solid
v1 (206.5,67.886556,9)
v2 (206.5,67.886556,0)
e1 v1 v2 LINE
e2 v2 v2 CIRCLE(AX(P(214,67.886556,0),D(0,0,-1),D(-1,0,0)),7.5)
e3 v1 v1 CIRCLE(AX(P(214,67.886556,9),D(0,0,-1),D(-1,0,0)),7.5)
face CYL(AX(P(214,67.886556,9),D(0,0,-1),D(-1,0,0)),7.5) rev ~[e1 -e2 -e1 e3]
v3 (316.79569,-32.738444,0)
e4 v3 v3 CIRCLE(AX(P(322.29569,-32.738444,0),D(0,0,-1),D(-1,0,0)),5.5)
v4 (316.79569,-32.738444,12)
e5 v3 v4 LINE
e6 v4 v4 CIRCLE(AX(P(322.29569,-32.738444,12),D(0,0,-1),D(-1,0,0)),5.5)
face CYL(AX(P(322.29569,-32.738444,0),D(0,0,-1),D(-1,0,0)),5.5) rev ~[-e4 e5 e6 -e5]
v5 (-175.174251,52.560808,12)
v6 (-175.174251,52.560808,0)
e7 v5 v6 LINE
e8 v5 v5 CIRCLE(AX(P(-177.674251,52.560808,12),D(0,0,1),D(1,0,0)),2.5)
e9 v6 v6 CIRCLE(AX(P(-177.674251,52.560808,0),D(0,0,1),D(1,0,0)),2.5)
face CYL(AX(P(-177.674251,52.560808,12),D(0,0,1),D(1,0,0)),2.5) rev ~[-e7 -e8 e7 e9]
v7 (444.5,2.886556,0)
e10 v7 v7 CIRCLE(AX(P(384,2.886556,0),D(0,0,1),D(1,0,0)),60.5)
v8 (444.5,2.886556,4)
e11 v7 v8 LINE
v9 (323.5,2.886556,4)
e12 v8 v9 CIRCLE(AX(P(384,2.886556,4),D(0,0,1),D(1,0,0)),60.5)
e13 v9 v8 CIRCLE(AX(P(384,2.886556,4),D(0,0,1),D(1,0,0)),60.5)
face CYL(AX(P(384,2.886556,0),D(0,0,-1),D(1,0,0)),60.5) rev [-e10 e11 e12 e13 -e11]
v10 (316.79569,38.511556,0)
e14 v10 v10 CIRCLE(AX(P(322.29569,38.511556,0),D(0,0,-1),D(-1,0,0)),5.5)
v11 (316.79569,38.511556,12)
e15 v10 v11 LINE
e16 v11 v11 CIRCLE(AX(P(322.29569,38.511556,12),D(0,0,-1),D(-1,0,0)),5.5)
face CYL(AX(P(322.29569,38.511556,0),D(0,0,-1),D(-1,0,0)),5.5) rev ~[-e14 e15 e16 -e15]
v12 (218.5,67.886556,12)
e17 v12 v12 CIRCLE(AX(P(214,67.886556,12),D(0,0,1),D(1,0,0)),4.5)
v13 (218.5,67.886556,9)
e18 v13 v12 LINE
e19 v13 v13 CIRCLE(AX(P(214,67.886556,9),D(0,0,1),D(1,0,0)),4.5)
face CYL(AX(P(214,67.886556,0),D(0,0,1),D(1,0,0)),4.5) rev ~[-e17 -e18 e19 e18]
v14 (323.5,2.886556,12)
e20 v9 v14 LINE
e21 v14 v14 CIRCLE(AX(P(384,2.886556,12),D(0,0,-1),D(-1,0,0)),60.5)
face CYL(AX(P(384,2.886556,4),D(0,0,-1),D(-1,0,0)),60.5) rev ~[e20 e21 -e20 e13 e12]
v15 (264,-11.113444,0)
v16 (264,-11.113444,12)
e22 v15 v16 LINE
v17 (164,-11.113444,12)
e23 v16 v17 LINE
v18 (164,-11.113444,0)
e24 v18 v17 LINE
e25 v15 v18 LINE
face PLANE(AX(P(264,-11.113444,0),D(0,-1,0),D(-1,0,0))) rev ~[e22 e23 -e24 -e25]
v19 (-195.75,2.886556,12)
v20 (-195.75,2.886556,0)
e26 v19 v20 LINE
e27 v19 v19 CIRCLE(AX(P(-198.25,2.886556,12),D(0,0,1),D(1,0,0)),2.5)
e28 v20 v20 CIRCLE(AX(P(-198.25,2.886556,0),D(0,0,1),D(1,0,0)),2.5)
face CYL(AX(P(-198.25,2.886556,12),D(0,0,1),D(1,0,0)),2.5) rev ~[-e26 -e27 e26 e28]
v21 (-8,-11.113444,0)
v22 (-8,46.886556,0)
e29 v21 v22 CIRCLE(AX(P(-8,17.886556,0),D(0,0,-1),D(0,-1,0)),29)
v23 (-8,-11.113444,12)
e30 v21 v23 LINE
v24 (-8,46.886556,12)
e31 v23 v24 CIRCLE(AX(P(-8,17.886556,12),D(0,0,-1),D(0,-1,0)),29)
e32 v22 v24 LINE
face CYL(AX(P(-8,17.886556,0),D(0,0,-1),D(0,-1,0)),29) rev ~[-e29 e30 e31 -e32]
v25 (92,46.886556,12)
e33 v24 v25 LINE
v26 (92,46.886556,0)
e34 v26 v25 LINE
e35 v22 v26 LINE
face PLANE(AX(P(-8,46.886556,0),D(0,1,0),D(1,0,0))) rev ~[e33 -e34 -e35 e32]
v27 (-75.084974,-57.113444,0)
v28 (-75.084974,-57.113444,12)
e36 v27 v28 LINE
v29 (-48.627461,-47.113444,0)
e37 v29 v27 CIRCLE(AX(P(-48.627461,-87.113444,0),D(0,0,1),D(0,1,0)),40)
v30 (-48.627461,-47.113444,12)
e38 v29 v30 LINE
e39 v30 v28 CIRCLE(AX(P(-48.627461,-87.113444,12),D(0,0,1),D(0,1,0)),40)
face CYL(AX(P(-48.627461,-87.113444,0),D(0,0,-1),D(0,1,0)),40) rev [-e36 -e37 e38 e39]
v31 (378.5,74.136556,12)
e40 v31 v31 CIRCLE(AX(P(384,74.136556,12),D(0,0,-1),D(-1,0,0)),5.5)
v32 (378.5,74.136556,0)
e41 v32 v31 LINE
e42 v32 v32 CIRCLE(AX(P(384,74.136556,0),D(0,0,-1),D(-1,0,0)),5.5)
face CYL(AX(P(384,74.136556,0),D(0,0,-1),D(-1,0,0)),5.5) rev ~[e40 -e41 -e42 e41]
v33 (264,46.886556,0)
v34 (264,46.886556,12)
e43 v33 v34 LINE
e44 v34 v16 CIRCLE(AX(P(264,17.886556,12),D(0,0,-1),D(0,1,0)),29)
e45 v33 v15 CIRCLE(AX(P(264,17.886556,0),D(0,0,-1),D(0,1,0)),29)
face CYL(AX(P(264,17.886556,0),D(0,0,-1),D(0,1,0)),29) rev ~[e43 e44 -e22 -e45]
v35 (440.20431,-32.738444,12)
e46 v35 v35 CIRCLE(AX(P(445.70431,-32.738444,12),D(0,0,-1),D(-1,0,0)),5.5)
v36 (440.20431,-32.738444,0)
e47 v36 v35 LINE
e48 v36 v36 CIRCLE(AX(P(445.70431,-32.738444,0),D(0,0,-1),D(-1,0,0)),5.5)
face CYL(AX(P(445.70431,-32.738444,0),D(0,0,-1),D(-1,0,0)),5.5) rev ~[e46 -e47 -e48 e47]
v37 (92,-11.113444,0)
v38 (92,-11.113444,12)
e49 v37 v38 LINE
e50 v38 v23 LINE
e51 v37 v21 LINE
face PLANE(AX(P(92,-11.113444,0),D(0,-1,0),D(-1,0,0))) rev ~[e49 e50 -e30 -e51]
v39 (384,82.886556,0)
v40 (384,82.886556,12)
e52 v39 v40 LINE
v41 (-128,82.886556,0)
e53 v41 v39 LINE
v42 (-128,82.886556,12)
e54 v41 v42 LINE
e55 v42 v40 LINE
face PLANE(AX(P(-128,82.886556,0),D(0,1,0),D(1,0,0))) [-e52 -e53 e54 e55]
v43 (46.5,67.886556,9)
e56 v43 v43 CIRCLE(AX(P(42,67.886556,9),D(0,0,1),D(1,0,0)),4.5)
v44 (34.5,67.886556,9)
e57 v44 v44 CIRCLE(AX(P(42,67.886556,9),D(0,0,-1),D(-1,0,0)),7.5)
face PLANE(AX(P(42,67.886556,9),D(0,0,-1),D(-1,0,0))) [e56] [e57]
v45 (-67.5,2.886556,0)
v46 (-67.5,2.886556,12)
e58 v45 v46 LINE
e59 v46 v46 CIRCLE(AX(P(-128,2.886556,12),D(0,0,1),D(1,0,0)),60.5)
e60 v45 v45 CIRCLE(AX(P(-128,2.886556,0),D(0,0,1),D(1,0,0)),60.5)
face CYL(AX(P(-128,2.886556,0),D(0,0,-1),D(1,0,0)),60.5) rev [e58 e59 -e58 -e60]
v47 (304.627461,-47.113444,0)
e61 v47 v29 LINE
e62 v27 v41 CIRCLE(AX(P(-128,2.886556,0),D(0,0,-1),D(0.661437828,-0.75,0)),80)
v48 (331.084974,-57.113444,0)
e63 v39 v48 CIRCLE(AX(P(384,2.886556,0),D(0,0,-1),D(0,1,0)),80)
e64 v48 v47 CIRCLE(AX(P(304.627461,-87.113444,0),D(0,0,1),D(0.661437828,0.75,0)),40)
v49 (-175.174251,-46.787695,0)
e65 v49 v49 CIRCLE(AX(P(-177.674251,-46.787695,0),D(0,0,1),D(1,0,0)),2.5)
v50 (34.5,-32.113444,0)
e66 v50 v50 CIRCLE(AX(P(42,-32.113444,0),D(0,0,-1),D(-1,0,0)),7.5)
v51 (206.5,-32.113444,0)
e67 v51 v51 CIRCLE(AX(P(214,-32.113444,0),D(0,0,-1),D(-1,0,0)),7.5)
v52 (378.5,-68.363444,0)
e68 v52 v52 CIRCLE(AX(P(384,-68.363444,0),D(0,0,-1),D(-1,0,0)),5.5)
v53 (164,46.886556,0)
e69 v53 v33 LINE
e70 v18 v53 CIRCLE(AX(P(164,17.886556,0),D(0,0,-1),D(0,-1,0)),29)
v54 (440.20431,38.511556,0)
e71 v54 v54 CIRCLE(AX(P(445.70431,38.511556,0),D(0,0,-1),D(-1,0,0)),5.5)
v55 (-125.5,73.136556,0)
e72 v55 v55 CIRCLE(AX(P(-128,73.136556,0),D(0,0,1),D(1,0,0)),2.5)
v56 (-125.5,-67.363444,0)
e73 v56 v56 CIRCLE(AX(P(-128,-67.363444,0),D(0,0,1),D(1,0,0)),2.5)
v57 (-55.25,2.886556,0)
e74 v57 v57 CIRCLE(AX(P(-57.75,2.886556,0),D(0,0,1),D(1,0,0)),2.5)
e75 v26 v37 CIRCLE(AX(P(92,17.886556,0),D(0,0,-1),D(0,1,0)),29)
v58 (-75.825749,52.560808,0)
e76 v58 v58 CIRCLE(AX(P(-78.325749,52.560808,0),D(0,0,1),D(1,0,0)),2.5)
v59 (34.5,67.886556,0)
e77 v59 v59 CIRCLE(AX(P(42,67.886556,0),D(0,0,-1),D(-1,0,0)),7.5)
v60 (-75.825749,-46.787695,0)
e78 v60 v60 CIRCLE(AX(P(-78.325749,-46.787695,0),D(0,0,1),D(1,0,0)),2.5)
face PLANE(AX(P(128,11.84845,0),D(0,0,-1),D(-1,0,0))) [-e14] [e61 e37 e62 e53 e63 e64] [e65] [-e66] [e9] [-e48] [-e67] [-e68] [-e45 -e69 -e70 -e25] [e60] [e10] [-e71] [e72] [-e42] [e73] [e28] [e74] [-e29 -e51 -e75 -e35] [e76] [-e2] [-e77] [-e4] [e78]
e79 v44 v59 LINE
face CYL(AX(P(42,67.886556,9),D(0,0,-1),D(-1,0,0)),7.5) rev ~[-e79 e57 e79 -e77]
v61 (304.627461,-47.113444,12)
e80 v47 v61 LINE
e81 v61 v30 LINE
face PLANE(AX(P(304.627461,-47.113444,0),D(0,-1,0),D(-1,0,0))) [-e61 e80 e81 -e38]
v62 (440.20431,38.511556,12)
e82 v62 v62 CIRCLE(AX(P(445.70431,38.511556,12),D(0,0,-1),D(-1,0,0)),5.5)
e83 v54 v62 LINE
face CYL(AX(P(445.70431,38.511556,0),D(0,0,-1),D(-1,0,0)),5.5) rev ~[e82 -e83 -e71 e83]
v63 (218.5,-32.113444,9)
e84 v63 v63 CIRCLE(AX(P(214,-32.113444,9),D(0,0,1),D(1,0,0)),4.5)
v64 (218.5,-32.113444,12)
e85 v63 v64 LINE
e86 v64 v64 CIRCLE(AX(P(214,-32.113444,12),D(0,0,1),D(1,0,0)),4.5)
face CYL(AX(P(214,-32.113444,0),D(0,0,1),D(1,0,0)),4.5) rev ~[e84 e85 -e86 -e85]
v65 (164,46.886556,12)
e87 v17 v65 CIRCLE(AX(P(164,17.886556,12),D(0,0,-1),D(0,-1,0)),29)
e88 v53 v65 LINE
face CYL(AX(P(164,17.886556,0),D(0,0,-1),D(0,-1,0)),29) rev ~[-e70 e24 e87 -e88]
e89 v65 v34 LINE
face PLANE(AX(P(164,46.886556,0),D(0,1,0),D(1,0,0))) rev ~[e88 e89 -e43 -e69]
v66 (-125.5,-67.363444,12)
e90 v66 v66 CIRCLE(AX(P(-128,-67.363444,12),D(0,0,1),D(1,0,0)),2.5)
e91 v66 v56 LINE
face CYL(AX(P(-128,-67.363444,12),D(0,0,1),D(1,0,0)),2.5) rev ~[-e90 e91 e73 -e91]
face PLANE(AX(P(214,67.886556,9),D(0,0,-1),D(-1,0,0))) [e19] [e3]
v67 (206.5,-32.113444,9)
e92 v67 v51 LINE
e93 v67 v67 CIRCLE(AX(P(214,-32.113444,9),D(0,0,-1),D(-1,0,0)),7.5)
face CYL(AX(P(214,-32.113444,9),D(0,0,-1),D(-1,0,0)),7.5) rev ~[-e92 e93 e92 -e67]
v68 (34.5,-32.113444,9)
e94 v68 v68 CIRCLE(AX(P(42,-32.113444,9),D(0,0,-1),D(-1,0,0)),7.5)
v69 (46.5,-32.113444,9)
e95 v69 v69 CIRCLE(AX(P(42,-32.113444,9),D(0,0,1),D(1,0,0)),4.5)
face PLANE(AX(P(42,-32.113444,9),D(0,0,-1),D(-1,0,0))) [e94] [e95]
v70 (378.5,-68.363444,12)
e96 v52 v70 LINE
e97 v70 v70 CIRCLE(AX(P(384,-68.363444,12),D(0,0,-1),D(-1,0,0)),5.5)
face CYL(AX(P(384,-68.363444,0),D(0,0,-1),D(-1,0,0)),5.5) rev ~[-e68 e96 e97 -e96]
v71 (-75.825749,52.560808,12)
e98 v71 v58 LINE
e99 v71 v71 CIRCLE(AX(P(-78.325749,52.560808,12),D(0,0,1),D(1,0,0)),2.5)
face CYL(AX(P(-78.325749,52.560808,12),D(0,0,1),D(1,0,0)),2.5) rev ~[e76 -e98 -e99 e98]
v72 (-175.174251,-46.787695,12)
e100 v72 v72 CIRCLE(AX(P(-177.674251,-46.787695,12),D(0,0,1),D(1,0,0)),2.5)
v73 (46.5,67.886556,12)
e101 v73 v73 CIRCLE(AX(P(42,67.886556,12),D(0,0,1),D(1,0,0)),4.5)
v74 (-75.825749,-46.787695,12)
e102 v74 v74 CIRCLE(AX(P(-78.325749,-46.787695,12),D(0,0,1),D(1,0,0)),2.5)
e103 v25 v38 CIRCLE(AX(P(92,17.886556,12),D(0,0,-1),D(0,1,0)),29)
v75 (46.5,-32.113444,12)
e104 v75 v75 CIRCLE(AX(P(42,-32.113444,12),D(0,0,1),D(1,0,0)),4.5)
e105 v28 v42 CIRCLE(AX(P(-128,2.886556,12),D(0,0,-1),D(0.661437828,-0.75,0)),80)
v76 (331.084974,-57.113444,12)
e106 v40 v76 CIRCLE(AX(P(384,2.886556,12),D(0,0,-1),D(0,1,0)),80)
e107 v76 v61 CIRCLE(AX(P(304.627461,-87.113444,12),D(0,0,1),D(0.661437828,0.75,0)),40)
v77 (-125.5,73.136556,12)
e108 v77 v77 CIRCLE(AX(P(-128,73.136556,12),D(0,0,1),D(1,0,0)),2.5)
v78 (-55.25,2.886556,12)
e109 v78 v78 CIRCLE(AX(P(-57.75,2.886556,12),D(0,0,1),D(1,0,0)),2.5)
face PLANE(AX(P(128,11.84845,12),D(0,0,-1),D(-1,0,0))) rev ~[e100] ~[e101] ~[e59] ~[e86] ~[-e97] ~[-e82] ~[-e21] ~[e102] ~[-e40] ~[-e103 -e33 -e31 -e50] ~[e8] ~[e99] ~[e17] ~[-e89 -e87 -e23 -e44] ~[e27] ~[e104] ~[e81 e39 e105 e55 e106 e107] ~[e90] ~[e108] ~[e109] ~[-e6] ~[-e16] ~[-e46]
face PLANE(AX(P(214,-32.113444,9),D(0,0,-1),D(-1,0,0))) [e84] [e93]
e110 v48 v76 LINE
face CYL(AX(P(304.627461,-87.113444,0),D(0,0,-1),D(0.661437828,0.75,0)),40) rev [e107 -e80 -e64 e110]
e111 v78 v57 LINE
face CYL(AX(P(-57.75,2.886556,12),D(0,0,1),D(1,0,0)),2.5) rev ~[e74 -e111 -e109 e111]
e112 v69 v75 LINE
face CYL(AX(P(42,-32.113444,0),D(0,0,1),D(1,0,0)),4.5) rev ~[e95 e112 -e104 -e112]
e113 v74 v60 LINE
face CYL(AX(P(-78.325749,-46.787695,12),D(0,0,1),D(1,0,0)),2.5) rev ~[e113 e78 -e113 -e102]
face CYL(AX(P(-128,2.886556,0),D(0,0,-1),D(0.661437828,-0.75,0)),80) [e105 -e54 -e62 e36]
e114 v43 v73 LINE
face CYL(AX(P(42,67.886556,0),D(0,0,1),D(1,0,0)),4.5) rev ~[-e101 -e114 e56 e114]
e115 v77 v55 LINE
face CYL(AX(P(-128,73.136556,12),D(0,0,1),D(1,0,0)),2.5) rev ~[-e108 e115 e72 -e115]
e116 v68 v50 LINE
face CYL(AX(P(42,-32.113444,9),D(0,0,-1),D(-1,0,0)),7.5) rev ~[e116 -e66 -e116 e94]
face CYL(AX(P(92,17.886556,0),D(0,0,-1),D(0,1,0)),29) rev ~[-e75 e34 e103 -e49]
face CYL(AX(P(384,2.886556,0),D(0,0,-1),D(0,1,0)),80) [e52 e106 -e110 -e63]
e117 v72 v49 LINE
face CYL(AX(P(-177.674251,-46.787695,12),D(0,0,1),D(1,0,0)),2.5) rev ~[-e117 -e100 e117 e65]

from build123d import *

# Parameters (mm, degrees)
SKETCH_1_R                   = 60.5
EXTRUDE_2_DEPTH              = 12
SKETCH_3_R                   = 60.5
CUT_EXTRUDE_2_DEPTH          = 4
HOLE_WIZARD_M8_2_D           = 9
HOLE_WIZARD_M8_2_CBORE_D     = 15
HOLE_WIZARD_M8_2_CBORE_DEPTH = 9
SKETCH_11_R                  = 18
CUT_EXTRUDE_5_DEPTH          = 472.497806181
SKETCH_12_R                  = 2.5
CUT_EXTRUDE_6_DEPTH          = 472.497806181
SKETCH_13_R                  = 60.5
CUT_EXTRUDE_7_DEPTH          = 472.412962521
SKETCH_14_R                  = 5.5
CUT_EXTRUDE_8_DEPTH          = 472.497806181


with BuildPart() as part:
    # 草图1 → 凸台-拉伸2 (new body)
    with BuildSketch(Plane.XY):
        with BuildLine():
            Line((-128, 82.886556409), (384, 82.886556409))
            ThreePointArc((384, 82.886556409), (458.833147735, -25.397714839), (331.084973779, -57.113443591))
            ThreePointArc((331.084973779, -57.113443591), (318.769596292, -49.696869724), (304.627460668, -47.113443591))
            Line((304.627460668, -47.113443591), (-48.627460668, -47.113443591))
            ThreePointArc((-48.627460668, -47.113443591), (-62.769596292, -49.696869724), (-75.084973779, -57.113443591))
            ThreePointArc((-75.084973779, -57.113443591), (-202.833147735, -25.397714839), (-128, 82.886556409))
        make_face()
        with Locations((-128, 2.886556409)):
            Circle(SKETCH_1_R, mode=Mode.SUBTRACT)
        with BuildLine():
            Line((-8, 46.886556409), (92, 46.886556409))
            ThreePointArc((92, 46.886556409), (121, 17.886556409), (92, -11.113443591))
            Line((92, -11.113443591), (-8, -11.113443591))
            ThreePointArc((-8, -11.113443591), (-37, 17.886556409), (-8, 46.886556409))
        make_face(mode=Mode.SUBTRACT)
        with BuildLine():
            Line((164, 46.886556409), (264, 46.886556409))
            ThreePointArc((264, 46.886556409), (293, 17.886556409), (264, -11.113443591))
            Line((264, -11.113443591), (164, -11.113443591))
            ThreePointArc((164, -11.113443591), (135, 17.886556409), (164, 46.886556409))
        make_face(mode=Mode.SUBTRACT)
    extrude(amount=EXTRUDE_2_DEPTH)

    # 草图3 → 切除-拉伸2 (cut)
    with BuildSketch(Plane.XY):
        with Locations((384, 2.886556409)):
            Circle(SKETCH_3_R)
    extrude(amount=CUT_EXTRUDE_2_DEPTH, mode=Mode.SUBTRACT)

    # M8 六角圆柱头螺钉的柱形沉头孔2 (through all)
    with Locations(Plane(origin=(0, 0, 0), x_dir=(-1, 0, 0), z_dir=(0, 0, -1))):
        with Locations((-214, 67.886556409), (-214, -32.113443591), (-42, 67.886556409), (-42, -32.113443591)):
            CounterBoreHole(HOLE_WIZARD_M8_2_D / 2, HOLE_WIZARD_M8_2_CBORE_D / 2, HOLE_WIZARD_M8_2_CBORE_DEPTH)

    # 草图11 → 切除-拉伸5 (cut, through all)
    with BuildSketch(Plane.XY):
        with Locations((384, 2.886556409)):
            Circle(SKETCH_11_R)
    extrude(amount=CUT_EXTRUDE_5_DEPTH, mode=Mode.SUBTRACT)

    # 草图12 → 切除-拉伸6 (cut, through all)
    with BuildSketch(Plane.XY.offset(12)):
        with Locations((-78.325748622, 52.560807787)):
            Circle(SKETCH_12_R)
        with Locations((-128, 73.136556409)):
            Circle(SKETCH_12_R)
        with Locations((-57.75, 2.886556409)):
            Circle(SKETCH_12_R)
        with Locations((-78.325748622, -46.78769497)):
            Circle(SKETCH_12_R)
        with Locations((-128, -67.363443591)):
            Circle(SKETCH_12_R)
        with Locations((-177.674251378, -46.78769497)):
            Circle(SKETCH_12_R)
        with Locations((-198.25, 2.886556409)):
            Circle(SKETCH_12_R)
        with Locations((-177.674251378, 52.560807787)):
            Circle(SKETCH_12_R)
    extrude(amount=-CUT_EXTRUDE_6_DEPTH, mode=Mode.SUBTRACT)

    # 草图13 → 切除-拉伸7 (cut, through all)
    with BuildSketch(Plane(origin=(0, 0, 4), x_dir=(-1, 0, 0), z_dir=(0, 0, -1))):
        with Locations((-384, 2.886556409)):
            Circle(SKETCH_13_R)
    extrude(amount=-CUT_EXTRUDE_7_DEPTH, mode=Mode.SUBTRACT)

    # 草图14 → 切除-拉伸8 (cut, through all)
    with BuildSketch(Plane(origin=(0, 0, 0), x_dir=(-1, 0, 0), z_dir=(0, 0, -1))):
        with Locations((-384, 74.136556409)):
            Circle(SKETCH_14_R)
        with Locations((-322.29568998, 38.511556409)):
            Circle(SKETCH_14_R)
        with Locations((-322.29568998, -32.738443591)):
            Circle(SKETCH_14_R)
        with Locations((-384, -68.363443591)):
            Circle(SKETCH_14_R)
        with Locations((-445.70431002, -32.738443591)):
            Circle(SKETCH_14_R)
        with Locations((-445.70431002, 38.511556409)):
            Circle(SKETCH_14_R)
    extrude(amount=-CUT_EXTRUDE_8_DEPTH, mode=Mode.SUBTRACT)


solid = part.part
